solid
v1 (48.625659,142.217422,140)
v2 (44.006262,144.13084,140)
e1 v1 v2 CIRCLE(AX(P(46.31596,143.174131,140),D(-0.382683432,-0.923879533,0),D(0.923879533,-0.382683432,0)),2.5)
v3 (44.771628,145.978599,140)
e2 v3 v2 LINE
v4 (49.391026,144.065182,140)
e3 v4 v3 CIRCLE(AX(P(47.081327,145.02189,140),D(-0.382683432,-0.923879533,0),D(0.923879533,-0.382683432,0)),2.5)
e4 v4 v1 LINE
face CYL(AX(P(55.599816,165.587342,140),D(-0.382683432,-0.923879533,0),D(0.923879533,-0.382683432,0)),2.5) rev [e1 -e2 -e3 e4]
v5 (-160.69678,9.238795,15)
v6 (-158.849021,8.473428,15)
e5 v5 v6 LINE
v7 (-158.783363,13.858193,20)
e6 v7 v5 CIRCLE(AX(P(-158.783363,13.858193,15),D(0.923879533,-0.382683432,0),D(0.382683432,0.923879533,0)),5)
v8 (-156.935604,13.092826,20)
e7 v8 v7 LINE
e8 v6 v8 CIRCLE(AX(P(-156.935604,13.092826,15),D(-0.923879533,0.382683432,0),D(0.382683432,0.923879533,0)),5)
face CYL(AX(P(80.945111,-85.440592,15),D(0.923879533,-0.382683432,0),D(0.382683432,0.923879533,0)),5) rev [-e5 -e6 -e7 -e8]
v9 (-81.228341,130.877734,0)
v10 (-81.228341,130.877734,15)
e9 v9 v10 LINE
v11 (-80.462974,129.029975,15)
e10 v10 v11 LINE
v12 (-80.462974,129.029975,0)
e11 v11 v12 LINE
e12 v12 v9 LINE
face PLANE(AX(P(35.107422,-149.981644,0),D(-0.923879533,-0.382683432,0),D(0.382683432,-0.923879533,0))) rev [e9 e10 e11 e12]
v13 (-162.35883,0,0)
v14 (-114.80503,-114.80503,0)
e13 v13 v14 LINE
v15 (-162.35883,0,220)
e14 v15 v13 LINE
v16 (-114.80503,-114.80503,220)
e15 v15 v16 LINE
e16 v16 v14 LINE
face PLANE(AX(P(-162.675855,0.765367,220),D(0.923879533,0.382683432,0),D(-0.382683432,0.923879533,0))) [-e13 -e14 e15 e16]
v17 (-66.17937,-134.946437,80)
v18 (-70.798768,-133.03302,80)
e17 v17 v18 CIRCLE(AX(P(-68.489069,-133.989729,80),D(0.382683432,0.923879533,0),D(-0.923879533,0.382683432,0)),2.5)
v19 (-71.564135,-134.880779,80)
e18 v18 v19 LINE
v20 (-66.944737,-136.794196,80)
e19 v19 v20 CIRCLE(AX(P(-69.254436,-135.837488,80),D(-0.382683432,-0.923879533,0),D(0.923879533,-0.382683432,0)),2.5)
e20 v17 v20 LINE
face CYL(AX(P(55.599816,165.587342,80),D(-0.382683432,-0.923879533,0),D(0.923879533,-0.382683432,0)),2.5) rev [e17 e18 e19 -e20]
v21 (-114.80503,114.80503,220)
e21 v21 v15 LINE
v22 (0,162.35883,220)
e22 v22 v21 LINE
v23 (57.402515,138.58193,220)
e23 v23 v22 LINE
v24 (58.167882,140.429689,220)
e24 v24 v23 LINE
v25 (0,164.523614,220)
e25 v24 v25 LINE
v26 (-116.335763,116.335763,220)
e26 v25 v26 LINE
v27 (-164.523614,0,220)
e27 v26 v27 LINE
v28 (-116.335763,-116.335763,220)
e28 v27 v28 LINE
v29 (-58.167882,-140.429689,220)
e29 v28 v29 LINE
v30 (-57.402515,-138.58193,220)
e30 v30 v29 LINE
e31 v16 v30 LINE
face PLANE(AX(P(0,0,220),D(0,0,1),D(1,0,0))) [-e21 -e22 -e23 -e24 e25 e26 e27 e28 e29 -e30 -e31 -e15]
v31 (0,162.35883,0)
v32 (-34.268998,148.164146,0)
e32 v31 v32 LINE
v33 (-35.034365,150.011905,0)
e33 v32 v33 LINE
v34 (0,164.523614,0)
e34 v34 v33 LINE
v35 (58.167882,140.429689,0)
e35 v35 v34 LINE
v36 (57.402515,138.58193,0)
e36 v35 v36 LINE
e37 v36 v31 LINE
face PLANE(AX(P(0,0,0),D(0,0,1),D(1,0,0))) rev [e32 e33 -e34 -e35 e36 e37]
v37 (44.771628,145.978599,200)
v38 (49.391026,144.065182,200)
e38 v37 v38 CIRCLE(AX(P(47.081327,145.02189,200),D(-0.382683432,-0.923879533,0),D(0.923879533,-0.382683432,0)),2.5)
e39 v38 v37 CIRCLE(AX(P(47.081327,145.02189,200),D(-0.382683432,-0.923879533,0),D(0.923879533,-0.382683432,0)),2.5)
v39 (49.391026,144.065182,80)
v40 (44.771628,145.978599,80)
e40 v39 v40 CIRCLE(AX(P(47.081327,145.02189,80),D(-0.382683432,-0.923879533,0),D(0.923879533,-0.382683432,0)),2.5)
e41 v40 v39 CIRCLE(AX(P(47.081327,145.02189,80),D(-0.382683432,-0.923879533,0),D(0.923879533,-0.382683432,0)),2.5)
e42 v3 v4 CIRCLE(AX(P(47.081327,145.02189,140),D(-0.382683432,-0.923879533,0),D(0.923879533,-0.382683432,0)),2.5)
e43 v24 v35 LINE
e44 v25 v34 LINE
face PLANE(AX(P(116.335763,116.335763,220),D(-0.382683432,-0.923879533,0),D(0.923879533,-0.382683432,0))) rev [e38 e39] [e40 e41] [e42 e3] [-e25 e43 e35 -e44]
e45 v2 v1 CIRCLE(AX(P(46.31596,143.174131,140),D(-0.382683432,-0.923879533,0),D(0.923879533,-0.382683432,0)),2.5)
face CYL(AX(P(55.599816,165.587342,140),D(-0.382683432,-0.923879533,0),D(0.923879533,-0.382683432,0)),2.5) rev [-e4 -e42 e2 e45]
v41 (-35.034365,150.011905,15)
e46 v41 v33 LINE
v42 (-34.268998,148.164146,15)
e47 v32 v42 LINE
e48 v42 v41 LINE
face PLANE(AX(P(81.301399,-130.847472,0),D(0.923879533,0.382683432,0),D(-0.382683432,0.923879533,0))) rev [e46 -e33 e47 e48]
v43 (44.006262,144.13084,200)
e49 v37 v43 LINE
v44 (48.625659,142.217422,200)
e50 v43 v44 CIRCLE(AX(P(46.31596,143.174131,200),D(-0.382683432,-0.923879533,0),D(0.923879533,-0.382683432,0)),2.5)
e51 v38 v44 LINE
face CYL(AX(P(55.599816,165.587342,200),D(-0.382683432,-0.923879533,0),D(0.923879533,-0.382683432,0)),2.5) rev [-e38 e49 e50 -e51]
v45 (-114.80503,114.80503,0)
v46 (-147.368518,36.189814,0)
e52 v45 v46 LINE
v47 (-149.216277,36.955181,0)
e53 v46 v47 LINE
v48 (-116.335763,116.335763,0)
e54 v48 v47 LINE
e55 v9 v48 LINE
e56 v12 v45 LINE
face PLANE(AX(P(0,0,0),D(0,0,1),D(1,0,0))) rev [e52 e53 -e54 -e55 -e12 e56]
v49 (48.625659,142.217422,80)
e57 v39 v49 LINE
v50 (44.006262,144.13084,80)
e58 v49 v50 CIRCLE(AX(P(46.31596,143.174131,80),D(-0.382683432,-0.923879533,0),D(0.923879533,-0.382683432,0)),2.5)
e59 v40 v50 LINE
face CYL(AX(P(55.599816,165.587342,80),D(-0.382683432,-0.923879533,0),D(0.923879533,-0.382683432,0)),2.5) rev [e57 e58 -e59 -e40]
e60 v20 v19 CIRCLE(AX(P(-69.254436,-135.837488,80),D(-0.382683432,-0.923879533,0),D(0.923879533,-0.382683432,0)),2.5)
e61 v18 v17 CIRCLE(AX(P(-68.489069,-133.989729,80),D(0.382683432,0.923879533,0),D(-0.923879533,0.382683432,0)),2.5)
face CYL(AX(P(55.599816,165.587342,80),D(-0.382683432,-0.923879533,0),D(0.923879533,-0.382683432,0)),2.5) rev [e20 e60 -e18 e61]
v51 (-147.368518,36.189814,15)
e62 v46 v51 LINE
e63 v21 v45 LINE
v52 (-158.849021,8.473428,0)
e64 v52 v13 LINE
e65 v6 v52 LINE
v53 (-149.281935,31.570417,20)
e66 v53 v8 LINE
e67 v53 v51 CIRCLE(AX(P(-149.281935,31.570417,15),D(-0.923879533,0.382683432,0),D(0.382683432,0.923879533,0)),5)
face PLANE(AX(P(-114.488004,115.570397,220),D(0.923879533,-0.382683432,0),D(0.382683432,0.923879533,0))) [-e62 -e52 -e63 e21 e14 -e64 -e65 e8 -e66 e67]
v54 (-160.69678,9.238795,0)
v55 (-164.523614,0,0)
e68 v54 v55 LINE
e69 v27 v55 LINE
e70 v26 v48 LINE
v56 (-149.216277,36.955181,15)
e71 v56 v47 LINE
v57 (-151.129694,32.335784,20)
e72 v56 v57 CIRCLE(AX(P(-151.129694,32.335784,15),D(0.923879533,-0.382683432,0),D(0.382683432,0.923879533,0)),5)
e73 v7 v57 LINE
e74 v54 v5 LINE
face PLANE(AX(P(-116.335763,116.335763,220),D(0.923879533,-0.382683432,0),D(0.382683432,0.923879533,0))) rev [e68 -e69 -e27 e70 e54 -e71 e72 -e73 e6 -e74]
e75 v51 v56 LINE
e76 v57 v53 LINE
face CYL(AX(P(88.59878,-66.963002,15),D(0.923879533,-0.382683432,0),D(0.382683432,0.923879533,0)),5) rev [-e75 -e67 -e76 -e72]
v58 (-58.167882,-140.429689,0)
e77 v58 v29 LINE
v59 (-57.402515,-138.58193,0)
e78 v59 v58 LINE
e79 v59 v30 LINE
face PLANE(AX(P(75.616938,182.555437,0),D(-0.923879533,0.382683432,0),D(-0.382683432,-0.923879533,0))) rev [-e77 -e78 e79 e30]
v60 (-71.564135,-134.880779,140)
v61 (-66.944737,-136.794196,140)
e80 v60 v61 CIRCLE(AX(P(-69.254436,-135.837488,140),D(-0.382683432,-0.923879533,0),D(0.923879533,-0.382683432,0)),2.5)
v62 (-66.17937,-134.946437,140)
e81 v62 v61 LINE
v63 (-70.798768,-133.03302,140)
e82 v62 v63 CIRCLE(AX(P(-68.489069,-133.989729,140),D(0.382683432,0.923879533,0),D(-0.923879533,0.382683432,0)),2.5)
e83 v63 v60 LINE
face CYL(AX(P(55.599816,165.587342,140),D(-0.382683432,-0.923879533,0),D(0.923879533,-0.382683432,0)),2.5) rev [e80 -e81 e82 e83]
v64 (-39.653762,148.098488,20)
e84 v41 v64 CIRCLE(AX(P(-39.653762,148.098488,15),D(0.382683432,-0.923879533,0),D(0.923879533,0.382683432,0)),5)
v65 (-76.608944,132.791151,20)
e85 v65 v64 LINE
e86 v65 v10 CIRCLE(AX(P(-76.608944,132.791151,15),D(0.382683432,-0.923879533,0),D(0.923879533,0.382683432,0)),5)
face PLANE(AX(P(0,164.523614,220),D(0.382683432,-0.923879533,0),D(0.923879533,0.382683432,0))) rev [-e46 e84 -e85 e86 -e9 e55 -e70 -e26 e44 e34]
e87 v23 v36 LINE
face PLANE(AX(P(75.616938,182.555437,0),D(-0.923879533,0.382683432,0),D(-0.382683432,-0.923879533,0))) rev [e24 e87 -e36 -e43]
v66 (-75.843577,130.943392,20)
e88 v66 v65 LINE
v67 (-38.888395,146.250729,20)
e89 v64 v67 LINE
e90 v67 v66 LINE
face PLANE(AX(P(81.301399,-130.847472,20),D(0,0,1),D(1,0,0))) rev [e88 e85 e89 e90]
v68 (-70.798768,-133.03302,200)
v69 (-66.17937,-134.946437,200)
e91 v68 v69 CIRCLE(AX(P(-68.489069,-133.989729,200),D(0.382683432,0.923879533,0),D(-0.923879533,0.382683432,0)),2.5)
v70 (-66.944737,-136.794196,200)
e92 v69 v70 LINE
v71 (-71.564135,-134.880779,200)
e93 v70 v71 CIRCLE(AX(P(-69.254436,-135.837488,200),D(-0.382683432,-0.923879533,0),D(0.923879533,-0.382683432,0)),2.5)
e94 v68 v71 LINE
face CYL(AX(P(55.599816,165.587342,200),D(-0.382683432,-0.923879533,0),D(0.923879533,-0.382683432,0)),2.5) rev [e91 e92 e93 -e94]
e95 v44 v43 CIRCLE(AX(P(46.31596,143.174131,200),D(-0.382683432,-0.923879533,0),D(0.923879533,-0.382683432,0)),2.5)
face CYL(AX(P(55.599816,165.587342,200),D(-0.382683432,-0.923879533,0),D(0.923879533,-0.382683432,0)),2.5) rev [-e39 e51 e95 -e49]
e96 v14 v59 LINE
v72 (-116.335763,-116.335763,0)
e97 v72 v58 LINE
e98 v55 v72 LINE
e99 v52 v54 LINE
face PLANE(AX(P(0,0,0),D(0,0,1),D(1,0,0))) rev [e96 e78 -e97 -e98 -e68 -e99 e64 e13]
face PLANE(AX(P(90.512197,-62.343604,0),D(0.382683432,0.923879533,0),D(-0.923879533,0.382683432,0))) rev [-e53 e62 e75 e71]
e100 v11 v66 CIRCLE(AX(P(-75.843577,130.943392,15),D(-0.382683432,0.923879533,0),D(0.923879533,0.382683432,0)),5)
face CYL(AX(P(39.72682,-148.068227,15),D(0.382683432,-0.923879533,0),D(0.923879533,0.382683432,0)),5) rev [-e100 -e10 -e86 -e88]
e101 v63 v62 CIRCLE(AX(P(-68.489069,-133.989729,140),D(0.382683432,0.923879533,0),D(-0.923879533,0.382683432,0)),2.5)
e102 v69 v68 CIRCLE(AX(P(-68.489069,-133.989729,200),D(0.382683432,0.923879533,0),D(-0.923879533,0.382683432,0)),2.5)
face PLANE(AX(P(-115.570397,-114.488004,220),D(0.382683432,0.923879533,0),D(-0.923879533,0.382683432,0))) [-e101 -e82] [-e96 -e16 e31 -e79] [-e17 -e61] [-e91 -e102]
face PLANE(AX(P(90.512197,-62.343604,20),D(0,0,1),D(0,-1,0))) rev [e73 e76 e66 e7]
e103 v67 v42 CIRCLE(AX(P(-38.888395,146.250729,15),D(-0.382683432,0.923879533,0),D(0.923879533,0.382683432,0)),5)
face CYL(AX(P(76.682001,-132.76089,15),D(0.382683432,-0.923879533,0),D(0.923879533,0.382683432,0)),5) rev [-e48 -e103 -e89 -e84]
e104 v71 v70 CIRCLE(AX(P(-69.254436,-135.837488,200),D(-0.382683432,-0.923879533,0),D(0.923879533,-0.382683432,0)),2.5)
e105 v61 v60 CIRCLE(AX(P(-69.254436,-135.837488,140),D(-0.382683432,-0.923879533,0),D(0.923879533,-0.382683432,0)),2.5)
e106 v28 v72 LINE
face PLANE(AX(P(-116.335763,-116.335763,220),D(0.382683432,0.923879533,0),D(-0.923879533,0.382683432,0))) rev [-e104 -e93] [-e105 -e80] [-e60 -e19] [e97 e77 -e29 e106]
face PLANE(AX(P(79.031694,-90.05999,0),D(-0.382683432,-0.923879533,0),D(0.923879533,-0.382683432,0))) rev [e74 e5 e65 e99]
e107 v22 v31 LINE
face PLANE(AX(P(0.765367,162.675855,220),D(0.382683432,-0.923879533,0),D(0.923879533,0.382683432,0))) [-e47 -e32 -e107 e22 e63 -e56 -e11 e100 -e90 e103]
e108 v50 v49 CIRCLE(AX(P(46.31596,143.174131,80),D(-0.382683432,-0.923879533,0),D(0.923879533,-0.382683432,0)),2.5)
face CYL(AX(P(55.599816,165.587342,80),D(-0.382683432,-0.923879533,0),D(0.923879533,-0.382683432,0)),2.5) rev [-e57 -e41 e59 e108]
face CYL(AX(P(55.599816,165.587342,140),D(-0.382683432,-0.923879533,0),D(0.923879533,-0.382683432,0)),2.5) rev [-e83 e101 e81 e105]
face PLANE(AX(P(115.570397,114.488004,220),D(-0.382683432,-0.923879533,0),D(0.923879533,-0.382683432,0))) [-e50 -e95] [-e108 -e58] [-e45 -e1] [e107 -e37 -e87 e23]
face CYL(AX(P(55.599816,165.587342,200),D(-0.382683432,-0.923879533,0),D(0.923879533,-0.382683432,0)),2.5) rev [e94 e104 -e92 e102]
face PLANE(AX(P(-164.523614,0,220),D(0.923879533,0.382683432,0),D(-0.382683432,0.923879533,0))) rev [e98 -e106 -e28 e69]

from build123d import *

# Parameters (mm, degrees)
BOSS_EXTRUDE1_DEPTH = 220
SHELL1_T            = -2
CUT_EXTRUDE1_DEPTH  = 321.212491043
SKETCH3_R           = 2.5
CUT_EXTRUDE2_DEPTH  = 394.612153142
SKETCH4_W           = 20
SKETCH4_H           = 30
CUT_EXTRUDE3_DEPTH  = 357.766015962
FILLET1_R           = 5
SKETCH5_W           = 50
SKETCH5_H           = 20
CUT_EXTRUDE4_DEPTH  = 376.254580252
FILLET2_R           = 5


with BuildPart() as part:
    # Sketch1 → Boss-Extrude1 (new body)
    with BuildSketch(Plane.XY):
        Polygon((-164.523614444, 0), (-116.335763439, -116.335763439), (0, -164.523614444), (116.335763439, -116.335763439), (164.523614444, 0), (116.335763439, 116.335763439), (0, 164.523614444), (-116.335763439, 116.335763439), align=None)
    extrude(amount=BOSS_EXTRUDE1_DEPTH)

    # Shell1
    shell1_openings = [part.faces().sort_by_distance(p)[0] for p in [
        (0, 0, 220),
        (0, 0, 0),
    ]]
    offset(amount=SHELL1_T, openings=shell1_openings, kind=Kind.INTERSECTION)

    # Sketch2 → Cut-Extrude1 (cut, through all)
    with BuildSketch(Plane.XY.offset(220)):
        Polygon((75.61693775, 182.555436661), (-82.042454152, -198.068005503), (95.714298716, -271.697263345), (253.373690618, 108.92617882), align=None)
    extrude(amount=-CUT_EXTRUDE1_DEPTH, mode=Mode.SUBTRACT)

    # Sketch3 → Cut-Extrude2 (cut, through all)
    with BuildSketch(Plane(origin=(-58.167881719, -140.429688942, 0), x_dir=(0.9238795325112961, -0.3826834323650676, 0), z_dir=(-0.3826834323650675, -0.923879532511296, 0))):
        with Locations((-12, 200)):
            Circle(SKETCH3_R)
        with Locations((-12, 140)):
            Circle(SKETCH3_R)
        with Locations((-12, 80)):
            Circle(SKETCH3_R)
    extrude(amount=-CUT_EXTRUDE2_DEPTH, mode=Mode.SUBTRACT)

    # Sketch4 → Cut-Extrude3 (cut, through all)
    with BuildSketch(Plane(origin=(-140.429688942, 58.167881719, 0), x_dir=(0, 0, 1), z_dir=(-0.9238795325112957, 0.3826834323650681, 0))):
        with Locations((10, -37.960461481)):
            Rectangle(SKETCH4_W, SKETCH4_H)
    extrude(amount=-CUT_EXTRUDE3_DEPTH, mode=Mode.SUBTRACT)

    # Fillet1
    fillet1_edges = [part.edges().sort_by_distance(p)[0] for p in [
        (-148.292397617, 36.572497868, 20),
        (-159.772900588, 8.856111893, 20),
    ]]
    fillet(fillet1_edges, radius=FILLET1_R)

    # Sketch5 → Cut-Extrude4 (cut, through all)
    with BuildSketch(Plane(origin=(-58.167881719, 140.429688942, 0), x_dir=(0.9238795325112777, 0.3826834323651116, 0), z_dir=(-0.38268343236511165, 0.9238795325112779, 0))):
        with Locations((0.039538519, -10)):
            Rectangle(SKETCH5_W, SKETCH5_H)
    extrude(amount=-CUT_EXTRUDE4_DEPTH, mode=Mode.SUBTRACT)

    # Fillet2
    fillet2_edges = [part.edges().sort_by_distance(p)[0] for p in [
        (-34.651681146, 149.088025955, 20),
        (-80.845657771, 129.953854336, 20),
    ]]
    fillet(fillet2_edges, radius=FILLET2_R)


solid = part.part
